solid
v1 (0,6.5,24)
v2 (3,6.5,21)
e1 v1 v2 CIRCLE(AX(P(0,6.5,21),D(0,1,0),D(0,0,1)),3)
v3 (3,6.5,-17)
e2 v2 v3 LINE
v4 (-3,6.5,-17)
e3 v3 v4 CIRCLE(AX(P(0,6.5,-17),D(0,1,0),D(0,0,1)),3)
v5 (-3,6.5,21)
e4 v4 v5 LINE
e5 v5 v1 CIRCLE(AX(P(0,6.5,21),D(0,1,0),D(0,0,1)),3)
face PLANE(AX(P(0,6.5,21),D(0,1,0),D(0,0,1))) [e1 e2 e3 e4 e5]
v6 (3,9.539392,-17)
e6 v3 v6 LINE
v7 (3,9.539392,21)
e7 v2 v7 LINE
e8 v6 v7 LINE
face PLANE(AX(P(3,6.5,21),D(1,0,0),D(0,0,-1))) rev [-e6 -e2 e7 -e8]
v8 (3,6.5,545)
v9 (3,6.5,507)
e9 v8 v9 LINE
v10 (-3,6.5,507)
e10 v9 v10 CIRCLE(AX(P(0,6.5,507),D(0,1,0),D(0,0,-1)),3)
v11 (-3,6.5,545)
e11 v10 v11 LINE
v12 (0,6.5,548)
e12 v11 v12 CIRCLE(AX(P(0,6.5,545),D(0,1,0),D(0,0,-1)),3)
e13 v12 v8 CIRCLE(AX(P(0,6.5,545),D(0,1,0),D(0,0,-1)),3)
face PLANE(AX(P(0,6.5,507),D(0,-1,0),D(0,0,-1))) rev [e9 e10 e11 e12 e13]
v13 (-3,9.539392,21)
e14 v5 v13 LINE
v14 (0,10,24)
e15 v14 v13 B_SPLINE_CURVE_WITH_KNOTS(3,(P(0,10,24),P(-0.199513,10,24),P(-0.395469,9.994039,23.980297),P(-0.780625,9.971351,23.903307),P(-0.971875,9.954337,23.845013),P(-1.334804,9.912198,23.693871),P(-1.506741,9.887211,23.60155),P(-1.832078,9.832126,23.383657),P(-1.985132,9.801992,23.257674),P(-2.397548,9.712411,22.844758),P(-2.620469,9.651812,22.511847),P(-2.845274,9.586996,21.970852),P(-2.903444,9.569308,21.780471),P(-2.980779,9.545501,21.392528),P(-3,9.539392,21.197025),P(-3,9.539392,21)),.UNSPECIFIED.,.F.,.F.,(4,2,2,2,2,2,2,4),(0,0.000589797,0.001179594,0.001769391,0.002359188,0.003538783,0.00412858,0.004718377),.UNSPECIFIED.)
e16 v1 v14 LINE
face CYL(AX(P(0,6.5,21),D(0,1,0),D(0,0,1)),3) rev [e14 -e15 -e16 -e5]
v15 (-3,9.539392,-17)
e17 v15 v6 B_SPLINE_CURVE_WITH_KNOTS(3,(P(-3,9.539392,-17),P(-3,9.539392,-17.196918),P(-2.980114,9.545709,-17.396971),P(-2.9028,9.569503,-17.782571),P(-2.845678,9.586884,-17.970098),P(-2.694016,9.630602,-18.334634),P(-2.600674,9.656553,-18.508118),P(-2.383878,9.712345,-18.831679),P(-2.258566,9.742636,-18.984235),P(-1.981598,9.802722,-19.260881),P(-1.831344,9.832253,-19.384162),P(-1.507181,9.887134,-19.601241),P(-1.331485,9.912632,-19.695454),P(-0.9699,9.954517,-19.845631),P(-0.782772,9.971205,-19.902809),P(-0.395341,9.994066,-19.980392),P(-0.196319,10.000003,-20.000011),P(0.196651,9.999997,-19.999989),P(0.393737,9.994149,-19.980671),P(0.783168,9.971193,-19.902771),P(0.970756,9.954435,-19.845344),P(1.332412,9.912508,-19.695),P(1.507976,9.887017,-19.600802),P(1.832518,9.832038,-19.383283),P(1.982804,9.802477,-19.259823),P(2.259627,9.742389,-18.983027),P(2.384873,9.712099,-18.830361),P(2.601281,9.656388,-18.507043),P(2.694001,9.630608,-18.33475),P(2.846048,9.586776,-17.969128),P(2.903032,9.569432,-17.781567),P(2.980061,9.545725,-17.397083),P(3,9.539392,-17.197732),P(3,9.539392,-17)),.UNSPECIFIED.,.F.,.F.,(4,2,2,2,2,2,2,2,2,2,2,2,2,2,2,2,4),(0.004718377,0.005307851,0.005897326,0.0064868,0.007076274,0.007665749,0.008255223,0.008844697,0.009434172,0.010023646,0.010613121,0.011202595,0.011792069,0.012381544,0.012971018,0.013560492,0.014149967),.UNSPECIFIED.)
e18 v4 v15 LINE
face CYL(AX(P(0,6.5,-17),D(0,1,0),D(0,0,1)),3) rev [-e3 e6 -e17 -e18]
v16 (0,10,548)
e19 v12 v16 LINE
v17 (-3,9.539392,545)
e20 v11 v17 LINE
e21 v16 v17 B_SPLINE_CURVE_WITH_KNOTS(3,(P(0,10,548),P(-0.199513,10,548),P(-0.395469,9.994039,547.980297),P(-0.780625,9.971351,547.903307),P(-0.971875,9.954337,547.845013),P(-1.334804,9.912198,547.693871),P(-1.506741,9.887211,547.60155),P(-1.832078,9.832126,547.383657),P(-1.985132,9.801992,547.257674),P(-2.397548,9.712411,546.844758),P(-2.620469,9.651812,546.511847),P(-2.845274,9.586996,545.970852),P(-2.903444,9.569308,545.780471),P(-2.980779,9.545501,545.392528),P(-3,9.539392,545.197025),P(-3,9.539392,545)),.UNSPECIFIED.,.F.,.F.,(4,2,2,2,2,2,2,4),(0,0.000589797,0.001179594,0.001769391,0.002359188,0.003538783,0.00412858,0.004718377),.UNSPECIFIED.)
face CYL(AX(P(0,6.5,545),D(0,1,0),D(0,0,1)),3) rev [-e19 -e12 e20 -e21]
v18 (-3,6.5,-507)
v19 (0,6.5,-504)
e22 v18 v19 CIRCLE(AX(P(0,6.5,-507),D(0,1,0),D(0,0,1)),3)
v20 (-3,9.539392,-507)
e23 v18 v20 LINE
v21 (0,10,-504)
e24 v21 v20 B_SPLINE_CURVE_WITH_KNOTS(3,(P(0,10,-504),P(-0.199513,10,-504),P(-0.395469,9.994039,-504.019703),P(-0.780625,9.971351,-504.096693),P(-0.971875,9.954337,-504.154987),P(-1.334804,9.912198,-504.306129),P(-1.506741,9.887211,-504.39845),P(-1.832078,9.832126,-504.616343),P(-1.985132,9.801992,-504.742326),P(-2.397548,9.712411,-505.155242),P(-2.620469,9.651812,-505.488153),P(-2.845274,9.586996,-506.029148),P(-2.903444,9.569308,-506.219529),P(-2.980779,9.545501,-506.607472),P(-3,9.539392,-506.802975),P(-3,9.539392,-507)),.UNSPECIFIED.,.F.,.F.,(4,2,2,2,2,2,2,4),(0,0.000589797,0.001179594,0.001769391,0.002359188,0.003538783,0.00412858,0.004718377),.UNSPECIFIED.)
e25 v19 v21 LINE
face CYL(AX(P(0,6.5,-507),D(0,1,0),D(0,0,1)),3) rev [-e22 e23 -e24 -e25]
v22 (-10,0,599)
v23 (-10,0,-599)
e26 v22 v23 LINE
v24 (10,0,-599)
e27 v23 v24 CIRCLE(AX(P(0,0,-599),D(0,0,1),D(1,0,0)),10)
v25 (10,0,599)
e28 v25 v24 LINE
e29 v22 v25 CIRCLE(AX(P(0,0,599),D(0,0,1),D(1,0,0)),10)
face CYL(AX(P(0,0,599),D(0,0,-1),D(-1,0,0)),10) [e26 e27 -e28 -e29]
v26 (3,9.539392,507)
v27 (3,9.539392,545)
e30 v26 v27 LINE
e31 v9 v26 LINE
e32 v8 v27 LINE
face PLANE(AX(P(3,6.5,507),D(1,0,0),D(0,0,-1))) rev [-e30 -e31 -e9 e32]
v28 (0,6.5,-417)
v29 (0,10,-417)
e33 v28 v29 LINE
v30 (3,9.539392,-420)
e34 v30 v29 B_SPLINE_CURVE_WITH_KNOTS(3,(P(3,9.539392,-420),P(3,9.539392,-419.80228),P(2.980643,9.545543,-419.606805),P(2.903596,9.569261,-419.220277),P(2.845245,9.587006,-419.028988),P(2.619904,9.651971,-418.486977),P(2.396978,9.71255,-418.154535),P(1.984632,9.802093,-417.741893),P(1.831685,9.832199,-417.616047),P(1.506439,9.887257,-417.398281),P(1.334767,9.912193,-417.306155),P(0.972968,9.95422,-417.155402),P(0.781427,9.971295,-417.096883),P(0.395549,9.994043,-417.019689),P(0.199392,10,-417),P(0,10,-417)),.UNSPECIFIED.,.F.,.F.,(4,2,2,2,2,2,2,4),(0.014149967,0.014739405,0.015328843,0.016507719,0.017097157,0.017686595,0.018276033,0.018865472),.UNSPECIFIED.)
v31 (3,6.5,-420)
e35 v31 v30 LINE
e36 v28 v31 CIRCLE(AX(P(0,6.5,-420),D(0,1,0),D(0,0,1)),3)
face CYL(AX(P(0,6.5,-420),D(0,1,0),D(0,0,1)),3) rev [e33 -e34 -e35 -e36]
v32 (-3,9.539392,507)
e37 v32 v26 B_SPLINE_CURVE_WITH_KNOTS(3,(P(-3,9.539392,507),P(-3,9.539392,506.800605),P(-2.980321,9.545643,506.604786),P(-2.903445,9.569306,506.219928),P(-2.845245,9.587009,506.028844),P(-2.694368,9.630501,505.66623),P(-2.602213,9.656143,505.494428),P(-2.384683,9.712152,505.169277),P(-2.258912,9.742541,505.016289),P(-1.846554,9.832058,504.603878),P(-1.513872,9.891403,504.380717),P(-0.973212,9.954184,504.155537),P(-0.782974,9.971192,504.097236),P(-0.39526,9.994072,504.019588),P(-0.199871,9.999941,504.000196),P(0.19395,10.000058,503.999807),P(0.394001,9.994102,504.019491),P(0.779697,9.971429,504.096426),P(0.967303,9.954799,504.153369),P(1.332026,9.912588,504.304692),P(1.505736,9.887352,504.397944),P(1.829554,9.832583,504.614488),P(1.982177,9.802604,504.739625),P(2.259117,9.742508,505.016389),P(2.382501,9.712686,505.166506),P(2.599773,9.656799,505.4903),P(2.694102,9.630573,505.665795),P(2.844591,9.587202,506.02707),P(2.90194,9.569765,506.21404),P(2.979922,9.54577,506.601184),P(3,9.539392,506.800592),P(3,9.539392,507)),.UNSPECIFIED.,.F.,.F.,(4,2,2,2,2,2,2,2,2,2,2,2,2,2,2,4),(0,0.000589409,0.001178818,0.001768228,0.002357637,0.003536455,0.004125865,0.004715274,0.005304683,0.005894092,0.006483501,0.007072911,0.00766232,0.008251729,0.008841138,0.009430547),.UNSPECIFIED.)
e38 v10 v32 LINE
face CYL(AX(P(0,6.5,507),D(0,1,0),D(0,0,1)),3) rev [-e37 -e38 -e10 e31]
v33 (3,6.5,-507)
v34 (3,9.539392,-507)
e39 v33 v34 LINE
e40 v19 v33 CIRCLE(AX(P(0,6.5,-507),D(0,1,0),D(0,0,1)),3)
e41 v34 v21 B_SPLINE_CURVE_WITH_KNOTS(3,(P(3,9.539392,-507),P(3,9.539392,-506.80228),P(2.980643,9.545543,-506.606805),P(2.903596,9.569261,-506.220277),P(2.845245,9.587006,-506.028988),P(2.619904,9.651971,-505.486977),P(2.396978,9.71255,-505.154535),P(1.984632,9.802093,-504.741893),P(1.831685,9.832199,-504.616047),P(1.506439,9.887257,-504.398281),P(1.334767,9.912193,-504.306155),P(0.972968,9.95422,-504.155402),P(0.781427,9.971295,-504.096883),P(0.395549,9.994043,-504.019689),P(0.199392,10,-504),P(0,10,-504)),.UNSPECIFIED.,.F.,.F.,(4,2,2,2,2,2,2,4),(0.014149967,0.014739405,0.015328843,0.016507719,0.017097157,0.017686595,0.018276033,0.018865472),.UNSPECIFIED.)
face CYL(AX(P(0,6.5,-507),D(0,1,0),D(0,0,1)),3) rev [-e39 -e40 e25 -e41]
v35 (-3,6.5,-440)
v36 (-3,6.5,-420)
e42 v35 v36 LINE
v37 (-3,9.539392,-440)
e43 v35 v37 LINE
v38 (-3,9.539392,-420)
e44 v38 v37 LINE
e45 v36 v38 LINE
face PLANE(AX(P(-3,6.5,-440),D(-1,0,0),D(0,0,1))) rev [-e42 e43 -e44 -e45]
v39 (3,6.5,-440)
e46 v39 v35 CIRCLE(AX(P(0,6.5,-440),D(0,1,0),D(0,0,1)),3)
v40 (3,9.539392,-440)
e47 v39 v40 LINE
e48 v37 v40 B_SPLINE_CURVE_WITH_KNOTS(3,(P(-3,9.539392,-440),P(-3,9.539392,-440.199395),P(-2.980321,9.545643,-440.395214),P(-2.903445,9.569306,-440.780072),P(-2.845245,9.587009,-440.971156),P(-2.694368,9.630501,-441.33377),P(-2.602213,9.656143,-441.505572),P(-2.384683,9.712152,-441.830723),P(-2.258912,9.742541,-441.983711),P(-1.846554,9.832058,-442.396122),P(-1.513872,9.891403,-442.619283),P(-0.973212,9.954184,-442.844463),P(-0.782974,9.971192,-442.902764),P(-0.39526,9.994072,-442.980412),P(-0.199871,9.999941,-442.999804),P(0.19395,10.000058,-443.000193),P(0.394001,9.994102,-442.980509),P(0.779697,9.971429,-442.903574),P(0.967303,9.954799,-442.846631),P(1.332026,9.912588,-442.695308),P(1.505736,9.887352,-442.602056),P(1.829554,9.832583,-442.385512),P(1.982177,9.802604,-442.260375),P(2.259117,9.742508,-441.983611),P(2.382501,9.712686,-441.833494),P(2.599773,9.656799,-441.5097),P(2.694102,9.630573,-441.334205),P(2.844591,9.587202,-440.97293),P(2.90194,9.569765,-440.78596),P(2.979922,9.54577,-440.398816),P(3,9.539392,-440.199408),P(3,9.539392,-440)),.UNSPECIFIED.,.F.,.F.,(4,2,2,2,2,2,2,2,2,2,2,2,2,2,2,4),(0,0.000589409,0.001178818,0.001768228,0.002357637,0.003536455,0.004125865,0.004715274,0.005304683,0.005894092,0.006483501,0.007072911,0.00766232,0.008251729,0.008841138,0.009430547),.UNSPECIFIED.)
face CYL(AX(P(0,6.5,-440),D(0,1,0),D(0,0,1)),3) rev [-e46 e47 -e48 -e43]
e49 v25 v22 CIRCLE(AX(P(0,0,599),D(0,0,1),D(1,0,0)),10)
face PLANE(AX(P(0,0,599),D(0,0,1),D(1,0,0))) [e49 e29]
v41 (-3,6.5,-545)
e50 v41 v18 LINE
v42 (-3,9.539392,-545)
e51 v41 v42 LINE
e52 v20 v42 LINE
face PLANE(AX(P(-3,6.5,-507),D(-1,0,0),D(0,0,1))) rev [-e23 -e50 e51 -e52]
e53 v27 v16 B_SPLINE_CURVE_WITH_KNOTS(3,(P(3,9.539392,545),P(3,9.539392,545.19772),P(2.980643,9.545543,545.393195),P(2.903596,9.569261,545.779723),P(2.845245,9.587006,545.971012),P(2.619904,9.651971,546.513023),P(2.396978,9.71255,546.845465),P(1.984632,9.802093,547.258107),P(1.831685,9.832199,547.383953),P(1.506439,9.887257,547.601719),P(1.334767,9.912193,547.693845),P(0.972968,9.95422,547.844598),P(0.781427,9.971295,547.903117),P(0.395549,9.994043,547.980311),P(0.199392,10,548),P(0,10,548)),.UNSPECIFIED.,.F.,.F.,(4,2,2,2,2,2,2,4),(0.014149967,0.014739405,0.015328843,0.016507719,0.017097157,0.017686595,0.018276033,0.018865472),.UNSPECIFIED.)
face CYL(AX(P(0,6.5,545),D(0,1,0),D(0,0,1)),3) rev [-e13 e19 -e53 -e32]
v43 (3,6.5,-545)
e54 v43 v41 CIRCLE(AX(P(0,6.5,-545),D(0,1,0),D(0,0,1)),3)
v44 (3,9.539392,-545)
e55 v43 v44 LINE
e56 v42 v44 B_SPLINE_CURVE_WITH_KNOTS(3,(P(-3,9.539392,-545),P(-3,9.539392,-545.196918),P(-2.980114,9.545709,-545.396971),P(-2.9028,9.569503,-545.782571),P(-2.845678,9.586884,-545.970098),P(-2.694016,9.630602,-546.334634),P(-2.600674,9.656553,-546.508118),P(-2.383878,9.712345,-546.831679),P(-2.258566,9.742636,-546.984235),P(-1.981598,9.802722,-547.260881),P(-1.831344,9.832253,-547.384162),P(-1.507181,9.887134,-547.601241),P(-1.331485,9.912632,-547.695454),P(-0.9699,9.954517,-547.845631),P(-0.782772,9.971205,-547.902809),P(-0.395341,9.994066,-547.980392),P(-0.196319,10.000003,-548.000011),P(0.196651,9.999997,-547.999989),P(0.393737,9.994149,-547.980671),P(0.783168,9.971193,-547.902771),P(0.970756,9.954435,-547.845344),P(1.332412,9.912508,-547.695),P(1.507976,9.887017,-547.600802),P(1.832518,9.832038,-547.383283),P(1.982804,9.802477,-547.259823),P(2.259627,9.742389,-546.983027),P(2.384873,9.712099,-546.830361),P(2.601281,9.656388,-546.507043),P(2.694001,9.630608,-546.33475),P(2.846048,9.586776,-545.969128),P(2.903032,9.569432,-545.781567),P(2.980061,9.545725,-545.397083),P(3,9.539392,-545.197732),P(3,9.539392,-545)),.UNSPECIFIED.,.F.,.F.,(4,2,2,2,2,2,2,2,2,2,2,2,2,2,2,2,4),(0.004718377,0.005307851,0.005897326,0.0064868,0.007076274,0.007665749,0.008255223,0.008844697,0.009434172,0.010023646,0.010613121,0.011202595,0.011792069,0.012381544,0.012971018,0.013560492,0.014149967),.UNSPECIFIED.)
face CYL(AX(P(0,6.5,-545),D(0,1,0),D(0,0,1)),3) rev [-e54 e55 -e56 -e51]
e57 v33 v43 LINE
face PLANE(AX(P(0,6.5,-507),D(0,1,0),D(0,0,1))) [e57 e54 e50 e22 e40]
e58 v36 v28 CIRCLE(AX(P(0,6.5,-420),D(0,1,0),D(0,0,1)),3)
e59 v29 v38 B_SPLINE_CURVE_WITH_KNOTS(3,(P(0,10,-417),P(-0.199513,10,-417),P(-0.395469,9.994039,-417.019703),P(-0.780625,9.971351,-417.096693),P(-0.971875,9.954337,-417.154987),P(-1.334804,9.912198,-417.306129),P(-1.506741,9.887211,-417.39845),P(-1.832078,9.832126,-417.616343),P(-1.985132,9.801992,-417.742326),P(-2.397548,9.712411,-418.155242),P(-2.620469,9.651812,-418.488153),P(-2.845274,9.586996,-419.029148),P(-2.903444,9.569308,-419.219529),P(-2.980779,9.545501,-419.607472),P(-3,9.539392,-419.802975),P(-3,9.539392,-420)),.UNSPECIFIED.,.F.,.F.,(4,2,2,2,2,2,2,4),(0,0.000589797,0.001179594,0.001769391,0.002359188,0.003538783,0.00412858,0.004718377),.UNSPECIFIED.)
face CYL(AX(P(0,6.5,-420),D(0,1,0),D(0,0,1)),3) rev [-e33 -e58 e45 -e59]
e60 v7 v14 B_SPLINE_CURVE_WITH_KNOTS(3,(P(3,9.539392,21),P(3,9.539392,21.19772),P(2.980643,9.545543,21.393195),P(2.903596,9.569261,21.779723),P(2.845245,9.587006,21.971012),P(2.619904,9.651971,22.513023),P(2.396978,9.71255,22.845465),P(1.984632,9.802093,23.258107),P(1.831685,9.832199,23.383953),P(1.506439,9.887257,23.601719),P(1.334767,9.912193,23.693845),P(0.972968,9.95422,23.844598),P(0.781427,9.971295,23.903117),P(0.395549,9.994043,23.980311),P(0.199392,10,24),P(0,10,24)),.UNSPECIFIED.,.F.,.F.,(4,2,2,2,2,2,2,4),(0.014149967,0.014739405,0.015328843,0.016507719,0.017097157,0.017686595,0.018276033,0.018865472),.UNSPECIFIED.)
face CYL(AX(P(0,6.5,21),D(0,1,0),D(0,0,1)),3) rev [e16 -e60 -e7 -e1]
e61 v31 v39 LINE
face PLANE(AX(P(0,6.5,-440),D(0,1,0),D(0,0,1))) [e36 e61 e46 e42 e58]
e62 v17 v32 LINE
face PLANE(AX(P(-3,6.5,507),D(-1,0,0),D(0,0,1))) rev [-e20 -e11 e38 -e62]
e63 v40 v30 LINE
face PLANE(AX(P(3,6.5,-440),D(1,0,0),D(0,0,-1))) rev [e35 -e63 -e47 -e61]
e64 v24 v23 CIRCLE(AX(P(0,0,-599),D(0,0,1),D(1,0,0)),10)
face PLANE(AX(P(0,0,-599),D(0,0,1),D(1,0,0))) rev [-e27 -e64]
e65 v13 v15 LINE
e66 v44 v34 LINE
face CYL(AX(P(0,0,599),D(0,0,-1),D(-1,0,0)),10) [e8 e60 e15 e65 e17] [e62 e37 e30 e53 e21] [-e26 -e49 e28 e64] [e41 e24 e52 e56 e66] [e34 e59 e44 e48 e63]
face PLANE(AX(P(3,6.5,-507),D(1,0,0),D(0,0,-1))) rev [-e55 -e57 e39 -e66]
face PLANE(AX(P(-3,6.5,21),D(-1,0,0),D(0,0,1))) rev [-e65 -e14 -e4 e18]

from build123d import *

# Parameters (mm, degrees)
SKETCH_1_R          = 10
EXTRUDE_1_DEPTH     = 599
CUT_EXTRUDE_START   = 10
CUT_EXTRUDE_3_DEPTH = 3.5


with BuildPart() as part:
    # 草图1 → 凸台-拉伸1 (new, symmetric)
    with BuildSketch(Plane.XY):
        Circle(SKETCH_1_R)
    extrude(amount=EXTRUDE_1_DEPTH, both=True)

    # 草图3 → 切除-拉伸3 (cut)
    with BuildSketch(Plane(origin=(0, 0, 0), x_dir=(1, 0, 0), z_dir=(0, 1, 0)).offset(CUT_EXTRUDE_START)):
        with BuildLine():
            Line((-3, 507), (-3, 545))
            ThreePointArc((-3, 545), (0, 548), (3, 545))
            Line((3, 545), (3, 507))
            ThreePointArc((3, 507), (0, 504), (-3, 507))
        make_face()
        with BuildLine():
            Line((-3, -507), (-3, -545))
            ThreePointArc((-3, -545), (0, -548), (3, -545))
            Line((3, -545), (3, -507))
            ThreePointArc((3, -507), (0, -504), (-3, -507))
        make_face()
        with BuildLine():
            Line((3, 440), (3, 420))
            ThreePointArc((3, 420), (0, 417), (-3, 420))
            Line((-3, 420), (-3, 440))
            ThreePointArc((-3, 440), (0, 443), (3, 440))
        make_face()
        with BuildLine():
            Line((-3, -21), (-3, 17))
            ThreePointArc((-3, 17), (0, 20), (3, 17))
            Line((3, 17), (3, -21))
            ThreePointArc((3, -21), (0, -24), (-3, -21))
        make_face()
    extrude(amount=-CUT_EXTRUDE_3_DEPTH, mode=Mode.SUBTRACT)


solid = part.part
